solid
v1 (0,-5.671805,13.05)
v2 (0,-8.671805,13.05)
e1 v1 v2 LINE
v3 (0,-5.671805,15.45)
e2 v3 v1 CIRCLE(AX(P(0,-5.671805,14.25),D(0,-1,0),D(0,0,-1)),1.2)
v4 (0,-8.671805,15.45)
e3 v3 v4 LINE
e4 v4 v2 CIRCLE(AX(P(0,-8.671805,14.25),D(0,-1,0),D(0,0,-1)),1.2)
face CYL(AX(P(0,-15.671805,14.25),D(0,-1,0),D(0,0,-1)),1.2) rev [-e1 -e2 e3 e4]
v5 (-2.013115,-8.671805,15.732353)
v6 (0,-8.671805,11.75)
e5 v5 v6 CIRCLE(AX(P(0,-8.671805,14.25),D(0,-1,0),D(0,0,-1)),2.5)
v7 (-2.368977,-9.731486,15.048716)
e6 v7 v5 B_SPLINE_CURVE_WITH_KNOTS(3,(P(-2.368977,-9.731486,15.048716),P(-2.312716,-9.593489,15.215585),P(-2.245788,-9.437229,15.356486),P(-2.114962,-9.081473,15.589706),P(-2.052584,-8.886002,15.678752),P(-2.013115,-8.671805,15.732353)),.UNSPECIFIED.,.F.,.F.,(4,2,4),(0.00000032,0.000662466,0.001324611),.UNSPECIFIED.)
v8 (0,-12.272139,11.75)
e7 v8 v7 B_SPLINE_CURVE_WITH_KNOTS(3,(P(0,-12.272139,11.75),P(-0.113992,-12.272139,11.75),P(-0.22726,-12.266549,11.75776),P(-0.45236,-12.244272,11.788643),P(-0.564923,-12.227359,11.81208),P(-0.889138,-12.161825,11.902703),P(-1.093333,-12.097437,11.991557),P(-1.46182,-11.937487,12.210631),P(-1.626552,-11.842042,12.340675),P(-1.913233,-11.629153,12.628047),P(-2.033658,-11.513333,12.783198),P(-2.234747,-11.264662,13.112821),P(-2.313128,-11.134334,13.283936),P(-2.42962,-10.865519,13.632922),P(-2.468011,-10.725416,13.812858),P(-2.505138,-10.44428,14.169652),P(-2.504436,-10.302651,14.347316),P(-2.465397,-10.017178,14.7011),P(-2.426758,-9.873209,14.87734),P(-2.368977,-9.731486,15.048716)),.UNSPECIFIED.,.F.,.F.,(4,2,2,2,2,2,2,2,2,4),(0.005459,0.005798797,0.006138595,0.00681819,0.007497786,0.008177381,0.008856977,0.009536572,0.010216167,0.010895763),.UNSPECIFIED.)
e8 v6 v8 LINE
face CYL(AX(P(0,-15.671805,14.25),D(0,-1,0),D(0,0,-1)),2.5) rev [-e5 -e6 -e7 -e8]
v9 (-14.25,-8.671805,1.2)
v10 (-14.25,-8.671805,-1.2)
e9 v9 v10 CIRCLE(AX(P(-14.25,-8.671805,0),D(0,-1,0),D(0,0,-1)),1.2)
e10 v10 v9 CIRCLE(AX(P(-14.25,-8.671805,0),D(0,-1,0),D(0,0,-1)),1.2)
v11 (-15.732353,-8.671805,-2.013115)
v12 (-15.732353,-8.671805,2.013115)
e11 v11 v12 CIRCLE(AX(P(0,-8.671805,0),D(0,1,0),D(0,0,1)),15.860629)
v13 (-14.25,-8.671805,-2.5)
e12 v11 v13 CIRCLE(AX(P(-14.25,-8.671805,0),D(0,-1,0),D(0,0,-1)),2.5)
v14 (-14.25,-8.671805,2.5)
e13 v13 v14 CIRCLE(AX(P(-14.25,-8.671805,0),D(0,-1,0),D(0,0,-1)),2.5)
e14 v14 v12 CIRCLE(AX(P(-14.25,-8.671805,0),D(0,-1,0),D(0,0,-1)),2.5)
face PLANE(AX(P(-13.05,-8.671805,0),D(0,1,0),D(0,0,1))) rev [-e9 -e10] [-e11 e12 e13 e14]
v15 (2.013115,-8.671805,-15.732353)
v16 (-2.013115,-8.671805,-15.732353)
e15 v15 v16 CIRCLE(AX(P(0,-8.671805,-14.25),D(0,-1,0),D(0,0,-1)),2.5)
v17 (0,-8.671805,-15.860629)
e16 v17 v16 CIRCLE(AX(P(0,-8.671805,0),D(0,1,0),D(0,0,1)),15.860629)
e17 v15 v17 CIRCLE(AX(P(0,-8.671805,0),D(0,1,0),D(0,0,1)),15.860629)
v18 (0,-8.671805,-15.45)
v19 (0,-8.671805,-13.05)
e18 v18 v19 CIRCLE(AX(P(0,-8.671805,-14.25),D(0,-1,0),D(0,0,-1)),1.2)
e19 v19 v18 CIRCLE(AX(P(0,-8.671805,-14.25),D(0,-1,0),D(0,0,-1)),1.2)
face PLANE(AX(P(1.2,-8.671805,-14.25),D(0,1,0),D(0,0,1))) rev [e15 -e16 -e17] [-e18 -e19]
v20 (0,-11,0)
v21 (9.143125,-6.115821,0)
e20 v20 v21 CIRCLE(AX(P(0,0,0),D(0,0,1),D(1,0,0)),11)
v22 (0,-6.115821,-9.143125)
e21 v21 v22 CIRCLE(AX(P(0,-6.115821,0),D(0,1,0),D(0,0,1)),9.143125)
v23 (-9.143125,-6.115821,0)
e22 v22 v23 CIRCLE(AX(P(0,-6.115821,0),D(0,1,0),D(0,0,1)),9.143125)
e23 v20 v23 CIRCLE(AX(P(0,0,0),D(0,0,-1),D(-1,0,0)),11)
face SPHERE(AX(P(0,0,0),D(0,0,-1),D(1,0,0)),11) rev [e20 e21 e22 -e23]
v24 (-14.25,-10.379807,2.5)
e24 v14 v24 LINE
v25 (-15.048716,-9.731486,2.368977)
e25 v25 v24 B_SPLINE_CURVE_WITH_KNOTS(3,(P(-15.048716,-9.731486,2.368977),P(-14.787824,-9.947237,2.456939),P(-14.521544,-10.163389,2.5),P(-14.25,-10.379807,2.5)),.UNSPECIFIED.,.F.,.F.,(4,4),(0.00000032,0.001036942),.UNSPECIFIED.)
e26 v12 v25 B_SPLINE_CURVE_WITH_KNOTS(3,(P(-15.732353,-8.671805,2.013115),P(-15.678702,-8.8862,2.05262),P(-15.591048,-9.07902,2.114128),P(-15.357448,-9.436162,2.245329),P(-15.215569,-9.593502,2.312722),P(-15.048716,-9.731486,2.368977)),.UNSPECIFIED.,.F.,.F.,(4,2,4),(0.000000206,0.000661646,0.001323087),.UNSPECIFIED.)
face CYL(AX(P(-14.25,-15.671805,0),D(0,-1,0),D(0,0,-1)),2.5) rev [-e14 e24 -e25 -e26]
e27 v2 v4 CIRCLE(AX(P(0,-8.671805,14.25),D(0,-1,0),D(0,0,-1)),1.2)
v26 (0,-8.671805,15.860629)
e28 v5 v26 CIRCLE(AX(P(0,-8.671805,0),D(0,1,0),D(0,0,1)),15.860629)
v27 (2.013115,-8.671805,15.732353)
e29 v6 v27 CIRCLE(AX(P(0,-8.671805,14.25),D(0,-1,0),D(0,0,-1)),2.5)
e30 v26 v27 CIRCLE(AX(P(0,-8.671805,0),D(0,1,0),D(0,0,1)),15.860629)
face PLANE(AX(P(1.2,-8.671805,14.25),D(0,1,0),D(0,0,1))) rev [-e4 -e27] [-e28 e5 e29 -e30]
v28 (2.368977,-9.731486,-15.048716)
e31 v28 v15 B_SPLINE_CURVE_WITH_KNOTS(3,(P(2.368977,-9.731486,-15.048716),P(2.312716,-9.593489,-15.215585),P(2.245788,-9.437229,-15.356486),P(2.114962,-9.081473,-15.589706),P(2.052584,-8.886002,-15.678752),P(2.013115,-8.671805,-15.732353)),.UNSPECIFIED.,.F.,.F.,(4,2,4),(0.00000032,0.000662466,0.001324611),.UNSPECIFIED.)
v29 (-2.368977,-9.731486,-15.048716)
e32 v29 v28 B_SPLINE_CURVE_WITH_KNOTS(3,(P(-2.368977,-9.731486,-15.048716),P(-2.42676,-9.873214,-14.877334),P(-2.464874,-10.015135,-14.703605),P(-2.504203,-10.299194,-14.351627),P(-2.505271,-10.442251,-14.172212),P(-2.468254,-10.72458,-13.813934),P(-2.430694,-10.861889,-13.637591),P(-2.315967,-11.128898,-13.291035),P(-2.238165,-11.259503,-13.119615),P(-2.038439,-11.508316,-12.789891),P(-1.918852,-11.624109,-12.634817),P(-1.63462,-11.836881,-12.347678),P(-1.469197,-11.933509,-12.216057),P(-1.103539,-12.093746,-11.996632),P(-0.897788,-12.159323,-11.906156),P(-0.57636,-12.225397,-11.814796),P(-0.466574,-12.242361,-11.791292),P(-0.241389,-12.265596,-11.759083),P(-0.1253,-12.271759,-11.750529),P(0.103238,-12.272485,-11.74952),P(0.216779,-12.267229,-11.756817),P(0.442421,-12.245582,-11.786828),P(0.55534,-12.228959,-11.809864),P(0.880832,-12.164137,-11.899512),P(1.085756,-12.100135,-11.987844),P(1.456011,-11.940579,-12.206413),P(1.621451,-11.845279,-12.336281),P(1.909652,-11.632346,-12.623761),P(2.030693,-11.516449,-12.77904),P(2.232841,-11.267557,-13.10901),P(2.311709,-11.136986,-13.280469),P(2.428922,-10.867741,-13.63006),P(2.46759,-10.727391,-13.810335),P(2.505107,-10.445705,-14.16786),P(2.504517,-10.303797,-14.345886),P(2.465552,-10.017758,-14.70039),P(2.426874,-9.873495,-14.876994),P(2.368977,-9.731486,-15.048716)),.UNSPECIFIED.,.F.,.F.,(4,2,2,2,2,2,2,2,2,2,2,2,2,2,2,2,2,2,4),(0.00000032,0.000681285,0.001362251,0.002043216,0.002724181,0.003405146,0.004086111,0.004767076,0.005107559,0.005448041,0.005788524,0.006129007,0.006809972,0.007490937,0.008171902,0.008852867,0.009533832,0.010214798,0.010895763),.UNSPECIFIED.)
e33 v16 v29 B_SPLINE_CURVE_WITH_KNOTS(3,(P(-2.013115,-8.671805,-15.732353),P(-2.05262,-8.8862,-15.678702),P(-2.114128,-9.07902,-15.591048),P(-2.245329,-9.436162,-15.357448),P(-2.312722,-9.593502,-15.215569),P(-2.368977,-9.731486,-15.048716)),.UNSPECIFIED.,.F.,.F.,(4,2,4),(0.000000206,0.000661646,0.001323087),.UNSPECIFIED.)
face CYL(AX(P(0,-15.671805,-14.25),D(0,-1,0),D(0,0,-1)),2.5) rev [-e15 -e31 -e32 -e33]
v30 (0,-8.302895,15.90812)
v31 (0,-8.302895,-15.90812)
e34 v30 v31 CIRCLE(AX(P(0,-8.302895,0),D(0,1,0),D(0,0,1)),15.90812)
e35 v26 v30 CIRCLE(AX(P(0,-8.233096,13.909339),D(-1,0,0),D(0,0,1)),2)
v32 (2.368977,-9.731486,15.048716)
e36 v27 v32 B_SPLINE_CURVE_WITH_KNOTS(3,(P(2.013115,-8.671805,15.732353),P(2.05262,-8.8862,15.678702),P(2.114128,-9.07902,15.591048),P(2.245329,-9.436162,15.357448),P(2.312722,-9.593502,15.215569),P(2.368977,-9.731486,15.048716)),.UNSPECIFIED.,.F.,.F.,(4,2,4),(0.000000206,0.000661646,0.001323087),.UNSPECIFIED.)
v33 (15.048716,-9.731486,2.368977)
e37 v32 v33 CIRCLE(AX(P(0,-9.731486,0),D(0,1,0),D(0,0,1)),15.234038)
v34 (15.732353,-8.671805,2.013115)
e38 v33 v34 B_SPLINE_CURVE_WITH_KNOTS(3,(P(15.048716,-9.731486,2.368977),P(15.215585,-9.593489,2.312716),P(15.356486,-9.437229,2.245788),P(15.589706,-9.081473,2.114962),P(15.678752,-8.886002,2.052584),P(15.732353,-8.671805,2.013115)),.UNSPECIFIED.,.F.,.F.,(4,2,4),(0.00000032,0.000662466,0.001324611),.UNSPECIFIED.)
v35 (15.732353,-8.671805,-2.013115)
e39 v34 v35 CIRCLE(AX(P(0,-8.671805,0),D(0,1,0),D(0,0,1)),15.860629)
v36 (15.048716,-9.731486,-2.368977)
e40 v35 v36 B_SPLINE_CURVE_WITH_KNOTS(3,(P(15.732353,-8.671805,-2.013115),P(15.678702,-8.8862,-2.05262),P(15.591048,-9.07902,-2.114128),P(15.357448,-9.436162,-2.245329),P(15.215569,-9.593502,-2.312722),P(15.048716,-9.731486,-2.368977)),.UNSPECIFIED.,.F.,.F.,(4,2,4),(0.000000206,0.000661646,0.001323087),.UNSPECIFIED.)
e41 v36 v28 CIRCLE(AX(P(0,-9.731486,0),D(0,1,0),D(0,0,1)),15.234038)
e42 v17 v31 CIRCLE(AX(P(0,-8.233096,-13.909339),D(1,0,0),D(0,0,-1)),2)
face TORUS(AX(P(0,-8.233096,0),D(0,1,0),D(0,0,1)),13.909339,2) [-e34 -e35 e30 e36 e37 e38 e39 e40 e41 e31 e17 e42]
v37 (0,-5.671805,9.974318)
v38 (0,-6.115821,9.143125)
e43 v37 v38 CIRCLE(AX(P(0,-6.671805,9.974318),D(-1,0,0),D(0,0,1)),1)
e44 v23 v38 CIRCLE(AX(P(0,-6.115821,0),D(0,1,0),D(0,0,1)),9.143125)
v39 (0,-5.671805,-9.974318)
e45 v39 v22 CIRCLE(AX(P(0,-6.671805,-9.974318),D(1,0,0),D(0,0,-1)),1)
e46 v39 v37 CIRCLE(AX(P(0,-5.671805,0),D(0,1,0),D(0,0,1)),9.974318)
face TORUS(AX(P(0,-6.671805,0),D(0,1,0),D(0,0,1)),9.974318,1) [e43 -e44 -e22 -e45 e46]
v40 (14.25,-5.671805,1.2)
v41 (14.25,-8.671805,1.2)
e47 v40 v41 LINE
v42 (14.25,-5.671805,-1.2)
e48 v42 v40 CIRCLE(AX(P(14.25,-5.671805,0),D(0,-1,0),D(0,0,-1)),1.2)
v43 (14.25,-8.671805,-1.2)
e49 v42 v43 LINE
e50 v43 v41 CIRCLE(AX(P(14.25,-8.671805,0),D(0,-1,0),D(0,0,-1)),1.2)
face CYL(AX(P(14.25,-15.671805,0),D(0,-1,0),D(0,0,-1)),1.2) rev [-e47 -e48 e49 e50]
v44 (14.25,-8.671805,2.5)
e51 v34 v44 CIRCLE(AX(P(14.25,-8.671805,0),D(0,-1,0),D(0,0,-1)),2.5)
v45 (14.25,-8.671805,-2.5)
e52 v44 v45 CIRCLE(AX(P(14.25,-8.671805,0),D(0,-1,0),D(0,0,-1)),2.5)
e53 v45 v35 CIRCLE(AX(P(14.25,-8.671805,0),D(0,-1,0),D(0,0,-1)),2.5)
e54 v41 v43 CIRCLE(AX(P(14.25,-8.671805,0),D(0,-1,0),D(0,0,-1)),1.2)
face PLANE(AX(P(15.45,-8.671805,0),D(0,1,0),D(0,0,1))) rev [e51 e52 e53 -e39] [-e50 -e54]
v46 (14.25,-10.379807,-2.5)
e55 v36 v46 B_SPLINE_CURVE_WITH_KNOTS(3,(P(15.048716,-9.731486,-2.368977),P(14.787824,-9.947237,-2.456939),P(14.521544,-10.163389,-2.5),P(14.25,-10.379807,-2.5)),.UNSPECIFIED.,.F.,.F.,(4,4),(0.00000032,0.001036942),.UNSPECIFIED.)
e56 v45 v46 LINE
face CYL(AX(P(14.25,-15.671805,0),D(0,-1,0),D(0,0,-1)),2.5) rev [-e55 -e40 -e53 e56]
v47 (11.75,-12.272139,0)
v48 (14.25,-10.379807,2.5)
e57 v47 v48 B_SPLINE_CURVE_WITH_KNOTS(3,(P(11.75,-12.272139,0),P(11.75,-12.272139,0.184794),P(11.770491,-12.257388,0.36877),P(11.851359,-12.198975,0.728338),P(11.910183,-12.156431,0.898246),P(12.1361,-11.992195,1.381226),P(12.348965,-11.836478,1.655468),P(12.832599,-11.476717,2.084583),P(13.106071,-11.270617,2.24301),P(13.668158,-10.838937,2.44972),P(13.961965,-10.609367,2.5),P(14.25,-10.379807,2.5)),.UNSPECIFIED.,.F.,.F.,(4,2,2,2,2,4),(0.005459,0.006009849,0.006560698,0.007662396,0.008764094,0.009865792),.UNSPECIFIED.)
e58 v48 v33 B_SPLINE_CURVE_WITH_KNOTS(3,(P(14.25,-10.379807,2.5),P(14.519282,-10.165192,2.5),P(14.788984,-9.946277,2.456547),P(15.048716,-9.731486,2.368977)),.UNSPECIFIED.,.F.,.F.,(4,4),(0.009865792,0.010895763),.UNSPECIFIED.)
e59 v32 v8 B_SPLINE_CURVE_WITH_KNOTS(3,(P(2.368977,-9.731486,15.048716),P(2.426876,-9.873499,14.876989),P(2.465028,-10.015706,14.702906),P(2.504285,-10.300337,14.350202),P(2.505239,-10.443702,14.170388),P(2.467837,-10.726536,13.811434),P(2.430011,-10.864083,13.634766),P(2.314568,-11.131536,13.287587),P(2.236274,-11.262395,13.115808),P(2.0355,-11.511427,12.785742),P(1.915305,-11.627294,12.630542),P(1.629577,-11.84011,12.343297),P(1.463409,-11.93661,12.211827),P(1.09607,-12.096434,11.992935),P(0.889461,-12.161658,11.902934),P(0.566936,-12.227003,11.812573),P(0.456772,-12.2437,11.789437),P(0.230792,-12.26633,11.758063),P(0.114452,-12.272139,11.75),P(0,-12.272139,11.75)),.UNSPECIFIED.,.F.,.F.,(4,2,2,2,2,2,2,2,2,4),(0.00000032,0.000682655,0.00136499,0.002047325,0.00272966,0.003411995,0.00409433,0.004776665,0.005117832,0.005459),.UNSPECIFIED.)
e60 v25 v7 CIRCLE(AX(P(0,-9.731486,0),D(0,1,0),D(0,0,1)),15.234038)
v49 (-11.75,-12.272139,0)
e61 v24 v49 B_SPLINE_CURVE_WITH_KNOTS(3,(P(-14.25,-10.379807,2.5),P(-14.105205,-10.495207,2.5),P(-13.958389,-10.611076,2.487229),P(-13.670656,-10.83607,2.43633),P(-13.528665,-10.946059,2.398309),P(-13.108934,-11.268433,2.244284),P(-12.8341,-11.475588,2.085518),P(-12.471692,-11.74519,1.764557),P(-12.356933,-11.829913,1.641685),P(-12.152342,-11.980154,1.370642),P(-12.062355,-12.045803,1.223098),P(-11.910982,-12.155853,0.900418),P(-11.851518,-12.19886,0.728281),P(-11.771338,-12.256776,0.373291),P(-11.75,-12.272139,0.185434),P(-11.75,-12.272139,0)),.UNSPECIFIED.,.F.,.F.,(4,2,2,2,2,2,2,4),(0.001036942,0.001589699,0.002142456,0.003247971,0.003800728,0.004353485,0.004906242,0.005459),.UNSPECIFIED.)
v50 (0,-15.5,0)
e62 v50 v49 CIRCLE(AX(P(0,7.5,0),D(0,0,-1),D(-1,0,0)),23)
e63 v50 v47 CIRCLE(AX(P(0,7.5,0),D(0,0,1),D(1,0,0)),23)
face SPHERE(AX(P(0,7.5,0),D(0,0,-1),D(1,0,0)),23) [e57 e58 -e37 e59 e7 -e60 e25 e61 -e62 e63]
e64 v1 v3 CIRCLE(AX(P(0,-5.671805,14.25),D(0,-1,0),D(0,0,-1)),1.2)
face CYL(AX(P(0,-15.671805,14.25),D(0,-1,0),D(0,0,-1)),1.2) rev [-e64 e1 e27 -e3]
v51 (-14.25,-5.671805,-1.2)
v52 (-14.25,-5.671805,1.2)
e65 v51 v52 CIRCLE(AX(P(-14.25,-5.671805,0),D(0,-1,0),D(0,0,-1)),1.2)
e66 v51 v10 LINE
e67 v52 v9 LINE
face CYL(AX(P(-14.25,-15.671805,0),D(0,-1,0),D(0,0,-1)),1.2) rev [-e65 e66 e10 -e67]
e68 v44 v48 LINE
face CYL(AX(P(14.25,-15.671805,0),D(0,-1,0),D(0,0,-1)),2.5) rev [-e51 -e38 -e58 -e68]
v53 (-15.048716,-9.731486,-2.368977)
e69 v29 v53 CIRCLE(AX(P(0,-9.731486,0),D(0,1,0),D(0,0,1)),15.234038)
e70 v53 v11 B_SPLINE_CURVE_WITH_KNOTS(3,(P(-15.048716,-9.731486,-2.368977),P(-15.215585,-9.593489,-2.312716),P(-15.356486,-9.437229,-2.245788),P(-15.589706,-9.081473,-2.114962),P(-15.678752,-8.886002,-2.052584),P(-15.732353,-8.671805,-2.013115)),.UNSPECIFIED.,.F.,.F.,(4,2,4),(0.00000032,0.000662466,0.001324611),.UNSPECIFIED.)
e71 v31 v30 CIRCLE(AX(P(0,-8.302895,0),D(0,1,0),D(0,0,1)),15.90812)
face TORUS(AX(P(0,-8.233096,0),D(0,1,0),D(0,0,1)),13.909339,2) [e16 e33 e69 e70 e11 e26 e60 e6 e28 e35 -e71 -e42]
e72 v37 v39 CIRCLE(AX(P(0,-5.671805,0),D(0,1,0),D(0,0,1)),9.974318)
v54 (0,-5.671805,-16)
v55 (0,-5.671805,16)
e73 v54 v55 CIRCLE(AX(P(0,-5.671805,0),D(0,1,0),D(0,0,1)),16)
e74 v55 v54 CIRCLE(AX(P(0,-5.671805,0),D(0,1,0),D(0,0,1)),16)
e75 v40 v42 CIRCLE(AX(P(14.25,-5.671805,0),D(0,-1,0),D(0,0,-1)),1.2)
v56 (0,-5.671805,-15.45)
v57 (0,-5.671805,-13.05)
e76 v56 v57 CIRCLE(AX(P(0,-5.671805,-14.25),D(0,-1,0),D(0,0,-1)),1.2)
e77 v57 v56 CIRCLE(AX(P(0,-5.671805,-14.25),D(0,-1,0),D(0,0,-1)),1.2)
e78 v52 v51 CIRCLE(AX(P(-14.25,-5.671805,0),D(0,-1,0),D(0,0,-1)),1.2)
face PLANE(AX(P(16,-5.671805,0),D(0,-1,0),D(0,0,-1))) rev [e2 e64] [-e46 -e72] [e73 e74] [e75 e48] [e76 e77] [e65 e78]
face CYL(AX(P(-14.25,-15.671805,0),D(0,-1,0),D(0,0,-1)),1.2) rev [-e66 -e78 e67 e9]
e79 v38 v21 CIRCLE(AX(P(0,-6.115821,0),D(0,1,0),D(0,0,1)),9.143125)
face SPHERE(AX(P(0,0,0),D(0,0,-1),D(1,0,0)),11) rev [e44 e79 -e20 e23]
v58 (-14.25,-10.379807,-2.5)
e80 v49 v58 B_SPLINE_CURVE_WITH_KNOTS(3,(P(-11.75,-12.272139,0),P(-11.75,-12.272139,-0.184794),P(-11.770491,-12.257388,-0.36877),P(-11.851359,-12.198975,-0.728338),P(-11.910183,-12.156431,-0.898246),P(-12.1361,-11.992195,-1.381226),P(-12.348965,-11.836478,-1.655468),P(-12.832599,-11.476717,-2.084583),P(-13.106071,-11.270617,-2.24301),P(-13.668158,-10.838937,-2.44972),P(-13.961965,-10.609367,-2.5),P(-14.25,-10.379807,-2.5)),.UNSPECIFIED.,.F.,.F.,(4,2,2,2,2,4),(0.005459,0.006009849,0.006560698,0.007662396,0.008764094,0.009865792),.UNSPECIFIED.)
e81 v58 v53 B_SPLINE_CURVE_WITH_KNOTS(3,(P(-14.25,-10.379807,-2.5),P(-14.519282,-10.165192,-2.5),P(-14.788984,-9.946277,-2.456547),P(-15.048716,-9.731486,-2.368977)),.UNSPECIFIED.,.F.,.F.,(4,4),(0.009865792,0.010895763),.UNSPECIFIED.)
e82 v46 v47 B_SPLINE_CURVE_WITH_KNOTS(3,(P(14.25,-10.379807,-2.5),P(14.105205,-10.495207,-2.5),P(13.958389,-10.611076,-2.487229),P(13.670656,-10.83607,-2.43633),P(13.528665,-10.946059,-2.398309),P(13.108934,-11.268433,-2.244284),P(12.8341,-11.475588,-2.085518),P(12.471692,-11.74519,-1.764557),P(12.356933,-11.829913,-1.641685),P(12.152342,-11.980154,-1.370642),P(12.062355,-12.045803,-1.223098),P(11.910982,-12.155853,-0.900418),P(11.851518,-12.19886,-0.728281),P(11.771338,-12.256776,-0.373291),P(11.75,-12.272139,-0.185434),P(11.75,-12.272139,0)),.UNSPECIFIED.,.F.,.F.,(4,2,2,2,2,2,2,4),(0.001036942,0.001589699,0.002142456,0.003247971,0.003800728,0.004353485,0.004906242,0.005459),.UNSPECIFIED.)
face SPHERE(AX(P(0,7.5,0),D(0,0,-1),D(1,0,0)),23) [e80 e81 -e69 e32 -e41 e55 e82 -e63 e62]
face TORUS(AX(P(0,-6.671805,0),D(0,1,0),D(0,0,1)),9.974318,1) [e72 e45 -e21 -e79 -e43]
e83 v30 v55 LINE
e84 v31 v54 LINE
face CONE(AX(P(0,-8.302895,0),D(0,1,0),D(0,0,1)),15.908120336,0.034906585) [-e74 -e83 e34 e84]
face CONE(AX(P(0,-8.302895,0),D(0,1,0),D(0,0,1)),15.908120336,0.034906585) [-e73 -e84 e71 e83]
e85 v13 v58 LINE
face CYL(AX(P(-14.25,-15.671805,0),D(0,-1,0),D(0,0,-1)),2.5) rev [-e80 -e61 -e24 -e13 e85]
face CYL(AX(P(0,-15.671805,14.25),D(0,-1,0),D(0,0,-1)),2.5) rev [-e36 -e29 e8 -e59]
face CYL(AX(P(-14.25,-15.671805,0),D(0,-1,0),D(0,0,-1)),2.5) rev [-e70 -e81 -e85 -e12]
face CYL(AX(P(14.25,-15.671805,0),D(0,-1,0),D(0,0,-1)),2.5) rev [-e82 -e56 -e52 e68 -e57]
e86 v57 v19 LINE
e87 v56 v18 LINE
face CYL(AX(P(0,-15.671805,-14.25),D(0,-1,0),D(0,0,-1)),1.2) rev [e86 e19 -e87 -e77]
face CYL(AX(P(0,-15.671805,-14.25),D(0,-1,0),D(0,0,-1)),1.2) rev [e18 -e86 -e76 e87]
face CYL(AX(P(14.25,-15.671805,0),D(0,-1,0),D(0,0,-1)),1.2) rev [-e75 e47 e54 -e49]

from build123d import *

# Parameters (mm, degrees)
HOLE_WIZARD_M2_1_D           = 2.4
HOLE_WIZARD_M2_1_CBORE_D     = 5
HOLE_WIZARD_M2_1_CBORE_DEPTH = 7


with BuildPart() as part:
    # 草图1 → 旋转1 (revolve)
    with BuildSketch(Plane.XY, mode=Mode.PRIVATE) as revolve_1_sk:
        with BuildLine():
            Line((0, -11), (0, -15.5))
            ThreePointArc((0, -15.5), (8.144809073, -14.009581241), (15.234037604, -9.731485667))
            ThreePointArc((15.234037604, -9.731485667), (15.718094855, -9.086559789), (15.908120336, -8.302894602))
            Line((15.908120336, -8.302894602), (16, -5.671805268))
            Line((16, -5.671805268), (9.974317744, -5.671805268))
            ThreePointArc((9.974317744, -5.671805268), (9.503140374, -5.789766785), (9.143124599, -6.115821496))
            ThreePointArc((9.143124599, -6.115821496), (5.182951068, -9.702423317), (0, -11))
        make_face()
    revolve(revolve_1_sk.sketch.rotate(Axis((0, -11, 0), (0, -1, 0)), 90), axis=Axis((0, -11, 0), (0, -1, 0)))

    # M2 六角头螺栓的柱形沉头孔1 (through all)
    with Locations(Plane.XZ.offset(15.671805268)):
        with Locations((-14.25, 0), (0, -14.25), (14.25, 0), (0, 14.25)):
            CounterBoreHole(HOLE_WIZARD_M2_1_D / 2, HOLE_WIZARD_M2_1_CBORE_D / 2, HOLE_WIZARD_M2_1_CBORE_DEPTH)


solid = part.part
